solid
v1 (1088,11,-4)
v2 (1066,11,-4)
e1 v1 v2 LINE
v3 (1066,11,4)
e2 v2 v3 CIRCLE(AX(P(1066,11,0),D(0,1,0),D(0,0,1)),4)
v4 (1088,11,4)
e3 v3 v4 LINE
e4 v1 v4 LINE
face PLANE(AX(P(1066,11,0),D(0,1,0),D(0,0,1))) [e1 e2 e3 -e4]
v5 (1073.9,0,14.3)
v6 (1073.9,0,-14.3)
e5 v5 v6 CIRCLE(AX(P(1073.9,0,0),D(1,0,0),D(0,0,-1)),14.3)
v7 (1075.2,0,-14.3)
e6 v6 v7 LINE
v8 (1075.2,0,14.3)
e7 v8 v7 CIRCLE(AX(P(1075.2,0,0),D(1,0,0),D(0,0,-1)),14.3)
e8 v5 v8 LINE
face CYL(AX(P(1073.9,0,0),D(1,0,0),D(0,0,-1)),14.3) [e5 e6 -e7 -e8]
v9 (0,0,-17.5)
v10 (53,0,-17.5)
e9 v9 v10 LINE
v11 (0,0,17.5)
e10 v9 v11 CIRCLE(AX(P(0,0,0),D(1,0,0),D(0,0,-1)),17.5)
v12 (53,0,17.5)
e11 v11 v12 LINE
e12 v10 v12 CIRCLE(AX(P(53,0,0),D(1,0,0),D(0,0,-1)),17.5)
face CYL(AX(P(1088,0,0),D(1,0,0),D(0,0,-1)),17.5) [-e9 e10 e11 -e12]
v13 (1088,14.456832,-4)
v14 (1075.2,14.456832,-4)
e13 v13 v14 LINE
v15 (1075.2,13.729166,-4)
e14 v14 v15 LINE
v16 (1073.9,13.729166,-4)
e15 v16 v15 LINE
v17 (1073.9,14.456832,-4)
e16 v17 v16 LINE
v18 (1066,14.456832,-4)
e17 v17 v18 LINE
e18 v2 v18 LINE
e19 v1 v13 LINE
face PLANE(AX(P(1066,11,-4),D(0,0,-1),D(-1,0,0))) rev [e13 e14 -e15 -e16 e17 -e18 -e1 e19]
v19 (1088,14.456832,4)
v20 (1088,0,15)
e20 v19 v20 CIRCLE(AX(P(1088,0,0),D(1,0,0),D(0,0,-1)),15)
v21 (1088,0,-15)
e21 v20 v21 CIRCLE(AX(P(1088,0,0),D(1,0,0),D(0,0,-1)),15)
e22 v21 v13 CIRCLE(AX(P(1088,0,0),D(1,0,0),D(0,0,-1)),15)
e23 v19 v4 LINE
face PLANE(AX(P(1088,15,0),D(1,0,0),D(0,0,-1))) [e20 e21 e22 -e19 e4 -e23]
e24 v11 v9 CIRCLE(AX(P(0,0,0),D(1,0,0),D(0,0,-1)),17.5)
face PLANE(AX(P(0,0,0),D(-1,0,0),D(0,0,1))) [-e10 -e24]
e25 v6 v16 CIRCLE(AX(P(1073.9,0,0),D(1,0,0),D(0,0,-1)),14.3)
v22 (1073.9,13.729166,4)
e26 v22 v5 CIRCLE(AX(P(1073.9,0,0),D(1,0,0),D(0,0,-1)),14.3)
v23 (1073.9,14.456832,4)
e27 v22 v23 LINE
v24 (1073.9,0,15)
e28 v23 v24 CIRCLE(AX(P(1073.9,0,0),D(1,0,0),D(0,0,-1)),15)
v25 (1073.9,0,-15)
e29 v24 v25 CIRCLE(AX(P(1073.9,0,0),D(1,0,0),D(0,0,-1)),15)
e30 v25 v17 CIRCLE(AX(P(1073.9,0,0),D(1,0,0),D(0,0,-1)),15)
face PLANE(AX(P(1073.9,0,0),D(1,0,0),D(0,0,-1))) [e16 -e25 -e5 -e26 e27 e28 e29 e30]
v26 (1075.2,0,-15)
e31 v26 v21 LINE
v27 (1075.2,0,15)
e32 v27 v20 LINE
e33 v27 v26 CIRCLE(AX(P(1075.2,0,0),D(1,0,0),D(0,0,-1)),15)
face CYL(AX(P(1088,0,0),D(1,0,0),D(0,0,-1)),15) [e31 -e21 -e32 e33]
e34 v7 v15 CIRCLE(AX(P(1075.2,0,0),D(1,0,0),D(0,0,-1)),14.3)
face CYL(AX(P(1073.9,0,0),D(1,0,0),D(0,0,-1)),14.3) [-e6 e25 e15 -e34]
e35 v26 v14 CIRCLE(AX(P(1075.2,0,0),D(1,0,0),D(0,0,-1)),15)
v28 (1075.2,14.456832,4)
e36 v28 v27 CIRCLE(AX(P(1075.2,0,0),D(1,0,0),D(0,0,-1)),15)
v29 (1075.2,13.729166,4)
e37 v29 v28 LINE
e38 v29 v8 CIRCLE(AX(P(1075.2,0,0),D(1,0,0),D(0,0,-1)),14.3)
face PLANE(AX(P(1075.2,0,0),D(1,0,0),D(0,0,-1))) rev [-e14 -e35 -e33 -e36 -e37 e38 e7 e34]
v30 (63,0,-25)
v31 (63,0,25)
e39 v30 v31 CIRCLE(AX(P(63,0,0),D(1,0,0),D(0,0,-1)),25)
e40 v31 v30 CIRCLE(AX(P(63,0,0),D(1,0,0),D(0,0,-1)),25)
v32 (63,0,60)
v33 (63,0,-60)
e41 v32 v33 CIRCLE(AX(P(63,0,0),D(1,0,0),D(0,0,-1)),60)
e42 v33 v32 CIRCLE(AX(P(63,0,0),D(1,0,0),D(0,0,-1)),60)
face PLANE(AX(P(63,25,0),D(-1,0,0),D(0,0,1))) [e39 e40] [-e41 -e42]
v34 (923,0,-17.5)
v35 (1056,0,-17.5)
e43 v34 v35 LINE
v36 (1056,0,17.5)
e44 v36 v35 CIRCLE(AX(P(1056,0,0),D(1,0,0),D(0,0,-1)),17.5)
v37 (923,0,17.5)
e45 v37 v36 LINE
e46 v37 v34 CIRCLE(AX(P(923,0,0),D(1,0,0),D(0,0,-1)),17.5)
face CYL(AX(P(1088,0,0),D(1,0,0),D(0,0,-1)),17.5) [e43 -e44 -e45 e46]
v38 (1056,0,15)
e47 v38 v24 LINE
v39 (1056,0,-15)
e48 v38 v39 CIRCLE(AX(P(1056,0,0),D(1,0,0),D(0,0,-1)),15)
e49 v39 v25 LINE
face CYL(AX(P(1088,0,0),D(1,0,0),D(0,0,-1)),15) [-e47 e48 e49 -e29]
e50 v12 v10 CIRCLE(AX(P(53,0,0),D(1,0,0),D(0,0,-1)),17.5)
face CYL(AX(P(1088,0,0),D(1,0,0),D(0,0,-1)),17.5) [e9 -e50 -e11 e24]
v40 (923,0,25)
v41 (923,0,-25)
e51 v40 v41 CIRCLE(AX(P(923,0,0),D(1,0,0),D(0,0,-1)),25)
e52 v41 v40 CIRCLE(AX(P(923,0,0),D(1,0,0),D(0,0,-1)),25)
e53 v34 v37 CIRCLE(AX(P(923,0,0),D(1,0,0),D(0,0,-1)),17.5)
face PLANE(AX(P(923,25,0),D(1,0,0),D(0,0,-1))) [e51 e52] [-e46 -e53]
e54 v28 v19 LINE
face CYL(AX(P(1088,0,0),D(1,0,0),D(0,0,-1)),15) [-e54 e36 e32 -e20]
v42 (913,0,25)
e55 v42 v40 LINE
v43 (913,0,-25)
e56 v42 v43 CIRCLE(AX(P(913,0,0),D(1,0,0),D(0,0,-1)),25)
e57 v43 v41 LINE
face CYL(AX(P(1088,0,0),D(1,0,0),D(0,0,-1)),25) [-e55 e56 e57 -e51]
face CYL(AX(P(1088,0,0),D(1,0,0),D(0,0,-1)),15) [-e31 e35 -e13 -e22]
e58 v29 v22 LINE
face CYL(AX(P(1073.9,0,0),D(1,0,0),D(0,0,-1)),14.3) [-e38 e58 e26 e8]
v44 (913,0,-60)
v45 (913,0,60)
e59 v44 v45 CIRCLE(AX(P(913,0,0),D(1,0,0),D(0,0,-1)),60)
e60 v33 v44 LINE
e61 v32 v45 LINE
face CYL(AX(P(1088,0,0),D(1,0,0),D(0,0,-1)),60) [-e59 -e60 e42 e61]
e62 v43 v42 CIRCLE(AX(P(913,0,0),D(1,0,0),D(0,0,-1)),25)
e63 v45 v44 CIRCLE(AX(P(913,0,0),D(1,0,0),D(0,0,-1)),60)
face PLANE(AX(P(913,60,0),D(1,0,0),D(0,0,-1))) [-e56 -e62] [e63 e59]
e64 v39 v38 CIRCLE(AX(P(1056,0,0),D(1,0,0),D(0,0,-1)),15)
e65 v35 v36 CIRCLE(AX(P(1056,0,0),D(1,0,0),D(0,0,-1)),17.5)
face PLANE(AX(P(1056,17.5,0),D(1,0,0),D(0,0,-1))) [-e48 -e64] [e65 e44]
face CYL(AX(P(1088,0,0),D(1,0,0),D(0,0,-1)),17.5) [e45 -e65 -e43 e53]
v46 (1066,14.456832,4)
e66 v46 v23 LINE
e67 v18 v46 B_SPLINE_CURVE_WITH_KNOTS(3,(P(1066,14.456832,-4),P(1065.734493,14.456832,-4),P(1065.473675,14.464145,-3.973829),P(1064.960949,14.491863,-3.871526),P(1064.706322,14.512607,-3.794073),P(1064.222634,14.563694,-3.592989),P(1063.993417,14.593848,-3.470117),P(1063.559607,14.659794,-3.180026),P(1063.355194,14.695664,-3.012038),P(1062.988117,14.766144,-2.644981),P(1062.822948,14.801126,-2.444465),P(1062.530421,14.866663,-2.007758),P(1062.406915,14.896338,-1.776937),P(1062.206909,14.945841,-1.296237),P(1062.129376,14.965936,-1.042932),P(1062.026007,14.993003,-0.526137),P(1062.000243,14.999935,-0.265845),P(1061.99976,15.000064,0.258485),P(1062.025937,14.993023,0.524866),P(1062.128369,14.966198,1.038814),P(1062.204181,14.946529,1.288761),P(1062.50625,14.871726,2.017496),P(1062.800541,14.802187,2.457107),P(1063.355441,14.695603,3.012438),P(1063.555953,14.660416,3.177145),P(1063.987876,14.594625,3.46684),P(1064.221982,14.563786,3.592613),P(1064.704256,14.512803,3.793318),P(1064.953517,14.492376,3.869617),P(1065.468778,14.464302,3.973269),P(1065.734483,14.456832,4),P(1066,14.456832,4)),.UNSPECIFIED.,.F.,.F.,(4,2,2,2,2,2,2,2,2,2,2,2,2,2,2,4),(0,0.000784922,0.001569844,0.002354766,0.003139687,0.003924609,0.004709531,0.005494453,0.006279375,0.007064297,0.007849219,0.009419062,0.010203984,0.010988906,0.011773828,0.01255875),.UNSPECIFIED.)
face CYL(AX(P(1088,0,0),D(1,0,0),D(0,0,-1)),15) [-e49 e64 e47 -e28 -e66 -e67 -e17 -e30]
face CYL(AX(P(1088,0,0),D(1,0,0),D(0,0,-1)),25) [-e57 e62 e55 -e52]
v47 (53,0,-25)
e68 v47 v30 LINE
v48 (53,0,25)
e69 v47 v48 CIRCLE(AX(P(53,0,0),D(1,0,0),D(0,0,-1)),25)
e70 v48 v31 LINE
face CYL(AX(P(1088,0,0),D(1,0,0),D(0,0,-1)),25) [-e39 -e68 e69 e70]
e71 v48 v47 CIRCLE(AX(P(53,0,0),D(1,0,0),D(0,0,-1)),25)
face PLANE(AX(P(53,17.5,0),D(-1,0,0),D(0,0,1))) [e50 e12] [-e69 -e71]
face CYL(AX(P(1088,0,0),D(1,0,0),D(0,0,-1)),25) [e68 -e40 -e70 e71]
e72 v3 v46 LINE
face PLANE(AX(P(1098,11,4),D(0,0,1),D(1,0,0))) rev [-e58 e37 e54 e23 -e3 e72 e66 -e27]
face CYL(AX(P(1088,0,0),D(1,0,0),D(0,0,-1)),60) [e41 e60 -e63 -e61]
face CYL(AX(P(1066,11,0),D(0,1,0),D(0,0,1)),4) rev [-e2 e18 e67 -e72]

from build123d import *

# Parameters (mm, degrees)
CUT_EXTRUDE_1_DEPTH = 4
SKETCH_3_R          = 15
SKETCH_3_R_2        = 14.3
CUT_EXTRUDE_2_DEPTH = 1.3


with BuildPart() as part:
    # 草图1 → 旋转1 (revolve)
    with BuildSketch(Plane.XY, mode=Mode.PRIVATE) as revolve_1_sk:
        Polygon((0, 0), (0, 17.5), (53, 17.5), (53, 25), (63, 25), (63, 60), (913, 60), (913, 25), (923, 25), (923, 17.5), (1056, 17.5), (1056, 15), (1088, 15), (1088, 0), align=None)
    revolve(revolve_1_sk.sketch.rotate(Axis((1088, 0, 0), (-1, 0, 0)), 90), axis=Axis((1088, 0, 0), (-1, 0, 0)))

    # 草图2 → 切除-拉伸1 (cut)
    with BuildSketch(Plane(origin=(0, 15, 0), x_dir=(1, 0, 0), z_dir=(0, 1, 0))):
        with BuildLine():
            Line((1066, 4), (1098, 4))
            Line((1098, 4), (1098, -4))
            Line((1098, -4), (1066, -4))
            ThreePointArc((1066, -4), (1062, 0), (1066, 4))
        make_face()
    extrude(amount=-CUT_EXTRUDE_1_DEPTH, mode=Mode.SUBTRACT)

    # 草图3 → 切除-拉伸2 (cut)
    with BuildSketch(Plane(origin=(1075.2, 0, 0), x_dir=(0, 0, -1), z_dir=(1, 0, 0))):
        Circle(SKETCH_3_R)
        Circle(SKETCH_3_R_2, mode=Mode.SUBTRACT)
    extrude(amount=-CUT_EXTRUDE_2_DEPTH, mode=Mode.SUBTRACT)


solid = part.part
